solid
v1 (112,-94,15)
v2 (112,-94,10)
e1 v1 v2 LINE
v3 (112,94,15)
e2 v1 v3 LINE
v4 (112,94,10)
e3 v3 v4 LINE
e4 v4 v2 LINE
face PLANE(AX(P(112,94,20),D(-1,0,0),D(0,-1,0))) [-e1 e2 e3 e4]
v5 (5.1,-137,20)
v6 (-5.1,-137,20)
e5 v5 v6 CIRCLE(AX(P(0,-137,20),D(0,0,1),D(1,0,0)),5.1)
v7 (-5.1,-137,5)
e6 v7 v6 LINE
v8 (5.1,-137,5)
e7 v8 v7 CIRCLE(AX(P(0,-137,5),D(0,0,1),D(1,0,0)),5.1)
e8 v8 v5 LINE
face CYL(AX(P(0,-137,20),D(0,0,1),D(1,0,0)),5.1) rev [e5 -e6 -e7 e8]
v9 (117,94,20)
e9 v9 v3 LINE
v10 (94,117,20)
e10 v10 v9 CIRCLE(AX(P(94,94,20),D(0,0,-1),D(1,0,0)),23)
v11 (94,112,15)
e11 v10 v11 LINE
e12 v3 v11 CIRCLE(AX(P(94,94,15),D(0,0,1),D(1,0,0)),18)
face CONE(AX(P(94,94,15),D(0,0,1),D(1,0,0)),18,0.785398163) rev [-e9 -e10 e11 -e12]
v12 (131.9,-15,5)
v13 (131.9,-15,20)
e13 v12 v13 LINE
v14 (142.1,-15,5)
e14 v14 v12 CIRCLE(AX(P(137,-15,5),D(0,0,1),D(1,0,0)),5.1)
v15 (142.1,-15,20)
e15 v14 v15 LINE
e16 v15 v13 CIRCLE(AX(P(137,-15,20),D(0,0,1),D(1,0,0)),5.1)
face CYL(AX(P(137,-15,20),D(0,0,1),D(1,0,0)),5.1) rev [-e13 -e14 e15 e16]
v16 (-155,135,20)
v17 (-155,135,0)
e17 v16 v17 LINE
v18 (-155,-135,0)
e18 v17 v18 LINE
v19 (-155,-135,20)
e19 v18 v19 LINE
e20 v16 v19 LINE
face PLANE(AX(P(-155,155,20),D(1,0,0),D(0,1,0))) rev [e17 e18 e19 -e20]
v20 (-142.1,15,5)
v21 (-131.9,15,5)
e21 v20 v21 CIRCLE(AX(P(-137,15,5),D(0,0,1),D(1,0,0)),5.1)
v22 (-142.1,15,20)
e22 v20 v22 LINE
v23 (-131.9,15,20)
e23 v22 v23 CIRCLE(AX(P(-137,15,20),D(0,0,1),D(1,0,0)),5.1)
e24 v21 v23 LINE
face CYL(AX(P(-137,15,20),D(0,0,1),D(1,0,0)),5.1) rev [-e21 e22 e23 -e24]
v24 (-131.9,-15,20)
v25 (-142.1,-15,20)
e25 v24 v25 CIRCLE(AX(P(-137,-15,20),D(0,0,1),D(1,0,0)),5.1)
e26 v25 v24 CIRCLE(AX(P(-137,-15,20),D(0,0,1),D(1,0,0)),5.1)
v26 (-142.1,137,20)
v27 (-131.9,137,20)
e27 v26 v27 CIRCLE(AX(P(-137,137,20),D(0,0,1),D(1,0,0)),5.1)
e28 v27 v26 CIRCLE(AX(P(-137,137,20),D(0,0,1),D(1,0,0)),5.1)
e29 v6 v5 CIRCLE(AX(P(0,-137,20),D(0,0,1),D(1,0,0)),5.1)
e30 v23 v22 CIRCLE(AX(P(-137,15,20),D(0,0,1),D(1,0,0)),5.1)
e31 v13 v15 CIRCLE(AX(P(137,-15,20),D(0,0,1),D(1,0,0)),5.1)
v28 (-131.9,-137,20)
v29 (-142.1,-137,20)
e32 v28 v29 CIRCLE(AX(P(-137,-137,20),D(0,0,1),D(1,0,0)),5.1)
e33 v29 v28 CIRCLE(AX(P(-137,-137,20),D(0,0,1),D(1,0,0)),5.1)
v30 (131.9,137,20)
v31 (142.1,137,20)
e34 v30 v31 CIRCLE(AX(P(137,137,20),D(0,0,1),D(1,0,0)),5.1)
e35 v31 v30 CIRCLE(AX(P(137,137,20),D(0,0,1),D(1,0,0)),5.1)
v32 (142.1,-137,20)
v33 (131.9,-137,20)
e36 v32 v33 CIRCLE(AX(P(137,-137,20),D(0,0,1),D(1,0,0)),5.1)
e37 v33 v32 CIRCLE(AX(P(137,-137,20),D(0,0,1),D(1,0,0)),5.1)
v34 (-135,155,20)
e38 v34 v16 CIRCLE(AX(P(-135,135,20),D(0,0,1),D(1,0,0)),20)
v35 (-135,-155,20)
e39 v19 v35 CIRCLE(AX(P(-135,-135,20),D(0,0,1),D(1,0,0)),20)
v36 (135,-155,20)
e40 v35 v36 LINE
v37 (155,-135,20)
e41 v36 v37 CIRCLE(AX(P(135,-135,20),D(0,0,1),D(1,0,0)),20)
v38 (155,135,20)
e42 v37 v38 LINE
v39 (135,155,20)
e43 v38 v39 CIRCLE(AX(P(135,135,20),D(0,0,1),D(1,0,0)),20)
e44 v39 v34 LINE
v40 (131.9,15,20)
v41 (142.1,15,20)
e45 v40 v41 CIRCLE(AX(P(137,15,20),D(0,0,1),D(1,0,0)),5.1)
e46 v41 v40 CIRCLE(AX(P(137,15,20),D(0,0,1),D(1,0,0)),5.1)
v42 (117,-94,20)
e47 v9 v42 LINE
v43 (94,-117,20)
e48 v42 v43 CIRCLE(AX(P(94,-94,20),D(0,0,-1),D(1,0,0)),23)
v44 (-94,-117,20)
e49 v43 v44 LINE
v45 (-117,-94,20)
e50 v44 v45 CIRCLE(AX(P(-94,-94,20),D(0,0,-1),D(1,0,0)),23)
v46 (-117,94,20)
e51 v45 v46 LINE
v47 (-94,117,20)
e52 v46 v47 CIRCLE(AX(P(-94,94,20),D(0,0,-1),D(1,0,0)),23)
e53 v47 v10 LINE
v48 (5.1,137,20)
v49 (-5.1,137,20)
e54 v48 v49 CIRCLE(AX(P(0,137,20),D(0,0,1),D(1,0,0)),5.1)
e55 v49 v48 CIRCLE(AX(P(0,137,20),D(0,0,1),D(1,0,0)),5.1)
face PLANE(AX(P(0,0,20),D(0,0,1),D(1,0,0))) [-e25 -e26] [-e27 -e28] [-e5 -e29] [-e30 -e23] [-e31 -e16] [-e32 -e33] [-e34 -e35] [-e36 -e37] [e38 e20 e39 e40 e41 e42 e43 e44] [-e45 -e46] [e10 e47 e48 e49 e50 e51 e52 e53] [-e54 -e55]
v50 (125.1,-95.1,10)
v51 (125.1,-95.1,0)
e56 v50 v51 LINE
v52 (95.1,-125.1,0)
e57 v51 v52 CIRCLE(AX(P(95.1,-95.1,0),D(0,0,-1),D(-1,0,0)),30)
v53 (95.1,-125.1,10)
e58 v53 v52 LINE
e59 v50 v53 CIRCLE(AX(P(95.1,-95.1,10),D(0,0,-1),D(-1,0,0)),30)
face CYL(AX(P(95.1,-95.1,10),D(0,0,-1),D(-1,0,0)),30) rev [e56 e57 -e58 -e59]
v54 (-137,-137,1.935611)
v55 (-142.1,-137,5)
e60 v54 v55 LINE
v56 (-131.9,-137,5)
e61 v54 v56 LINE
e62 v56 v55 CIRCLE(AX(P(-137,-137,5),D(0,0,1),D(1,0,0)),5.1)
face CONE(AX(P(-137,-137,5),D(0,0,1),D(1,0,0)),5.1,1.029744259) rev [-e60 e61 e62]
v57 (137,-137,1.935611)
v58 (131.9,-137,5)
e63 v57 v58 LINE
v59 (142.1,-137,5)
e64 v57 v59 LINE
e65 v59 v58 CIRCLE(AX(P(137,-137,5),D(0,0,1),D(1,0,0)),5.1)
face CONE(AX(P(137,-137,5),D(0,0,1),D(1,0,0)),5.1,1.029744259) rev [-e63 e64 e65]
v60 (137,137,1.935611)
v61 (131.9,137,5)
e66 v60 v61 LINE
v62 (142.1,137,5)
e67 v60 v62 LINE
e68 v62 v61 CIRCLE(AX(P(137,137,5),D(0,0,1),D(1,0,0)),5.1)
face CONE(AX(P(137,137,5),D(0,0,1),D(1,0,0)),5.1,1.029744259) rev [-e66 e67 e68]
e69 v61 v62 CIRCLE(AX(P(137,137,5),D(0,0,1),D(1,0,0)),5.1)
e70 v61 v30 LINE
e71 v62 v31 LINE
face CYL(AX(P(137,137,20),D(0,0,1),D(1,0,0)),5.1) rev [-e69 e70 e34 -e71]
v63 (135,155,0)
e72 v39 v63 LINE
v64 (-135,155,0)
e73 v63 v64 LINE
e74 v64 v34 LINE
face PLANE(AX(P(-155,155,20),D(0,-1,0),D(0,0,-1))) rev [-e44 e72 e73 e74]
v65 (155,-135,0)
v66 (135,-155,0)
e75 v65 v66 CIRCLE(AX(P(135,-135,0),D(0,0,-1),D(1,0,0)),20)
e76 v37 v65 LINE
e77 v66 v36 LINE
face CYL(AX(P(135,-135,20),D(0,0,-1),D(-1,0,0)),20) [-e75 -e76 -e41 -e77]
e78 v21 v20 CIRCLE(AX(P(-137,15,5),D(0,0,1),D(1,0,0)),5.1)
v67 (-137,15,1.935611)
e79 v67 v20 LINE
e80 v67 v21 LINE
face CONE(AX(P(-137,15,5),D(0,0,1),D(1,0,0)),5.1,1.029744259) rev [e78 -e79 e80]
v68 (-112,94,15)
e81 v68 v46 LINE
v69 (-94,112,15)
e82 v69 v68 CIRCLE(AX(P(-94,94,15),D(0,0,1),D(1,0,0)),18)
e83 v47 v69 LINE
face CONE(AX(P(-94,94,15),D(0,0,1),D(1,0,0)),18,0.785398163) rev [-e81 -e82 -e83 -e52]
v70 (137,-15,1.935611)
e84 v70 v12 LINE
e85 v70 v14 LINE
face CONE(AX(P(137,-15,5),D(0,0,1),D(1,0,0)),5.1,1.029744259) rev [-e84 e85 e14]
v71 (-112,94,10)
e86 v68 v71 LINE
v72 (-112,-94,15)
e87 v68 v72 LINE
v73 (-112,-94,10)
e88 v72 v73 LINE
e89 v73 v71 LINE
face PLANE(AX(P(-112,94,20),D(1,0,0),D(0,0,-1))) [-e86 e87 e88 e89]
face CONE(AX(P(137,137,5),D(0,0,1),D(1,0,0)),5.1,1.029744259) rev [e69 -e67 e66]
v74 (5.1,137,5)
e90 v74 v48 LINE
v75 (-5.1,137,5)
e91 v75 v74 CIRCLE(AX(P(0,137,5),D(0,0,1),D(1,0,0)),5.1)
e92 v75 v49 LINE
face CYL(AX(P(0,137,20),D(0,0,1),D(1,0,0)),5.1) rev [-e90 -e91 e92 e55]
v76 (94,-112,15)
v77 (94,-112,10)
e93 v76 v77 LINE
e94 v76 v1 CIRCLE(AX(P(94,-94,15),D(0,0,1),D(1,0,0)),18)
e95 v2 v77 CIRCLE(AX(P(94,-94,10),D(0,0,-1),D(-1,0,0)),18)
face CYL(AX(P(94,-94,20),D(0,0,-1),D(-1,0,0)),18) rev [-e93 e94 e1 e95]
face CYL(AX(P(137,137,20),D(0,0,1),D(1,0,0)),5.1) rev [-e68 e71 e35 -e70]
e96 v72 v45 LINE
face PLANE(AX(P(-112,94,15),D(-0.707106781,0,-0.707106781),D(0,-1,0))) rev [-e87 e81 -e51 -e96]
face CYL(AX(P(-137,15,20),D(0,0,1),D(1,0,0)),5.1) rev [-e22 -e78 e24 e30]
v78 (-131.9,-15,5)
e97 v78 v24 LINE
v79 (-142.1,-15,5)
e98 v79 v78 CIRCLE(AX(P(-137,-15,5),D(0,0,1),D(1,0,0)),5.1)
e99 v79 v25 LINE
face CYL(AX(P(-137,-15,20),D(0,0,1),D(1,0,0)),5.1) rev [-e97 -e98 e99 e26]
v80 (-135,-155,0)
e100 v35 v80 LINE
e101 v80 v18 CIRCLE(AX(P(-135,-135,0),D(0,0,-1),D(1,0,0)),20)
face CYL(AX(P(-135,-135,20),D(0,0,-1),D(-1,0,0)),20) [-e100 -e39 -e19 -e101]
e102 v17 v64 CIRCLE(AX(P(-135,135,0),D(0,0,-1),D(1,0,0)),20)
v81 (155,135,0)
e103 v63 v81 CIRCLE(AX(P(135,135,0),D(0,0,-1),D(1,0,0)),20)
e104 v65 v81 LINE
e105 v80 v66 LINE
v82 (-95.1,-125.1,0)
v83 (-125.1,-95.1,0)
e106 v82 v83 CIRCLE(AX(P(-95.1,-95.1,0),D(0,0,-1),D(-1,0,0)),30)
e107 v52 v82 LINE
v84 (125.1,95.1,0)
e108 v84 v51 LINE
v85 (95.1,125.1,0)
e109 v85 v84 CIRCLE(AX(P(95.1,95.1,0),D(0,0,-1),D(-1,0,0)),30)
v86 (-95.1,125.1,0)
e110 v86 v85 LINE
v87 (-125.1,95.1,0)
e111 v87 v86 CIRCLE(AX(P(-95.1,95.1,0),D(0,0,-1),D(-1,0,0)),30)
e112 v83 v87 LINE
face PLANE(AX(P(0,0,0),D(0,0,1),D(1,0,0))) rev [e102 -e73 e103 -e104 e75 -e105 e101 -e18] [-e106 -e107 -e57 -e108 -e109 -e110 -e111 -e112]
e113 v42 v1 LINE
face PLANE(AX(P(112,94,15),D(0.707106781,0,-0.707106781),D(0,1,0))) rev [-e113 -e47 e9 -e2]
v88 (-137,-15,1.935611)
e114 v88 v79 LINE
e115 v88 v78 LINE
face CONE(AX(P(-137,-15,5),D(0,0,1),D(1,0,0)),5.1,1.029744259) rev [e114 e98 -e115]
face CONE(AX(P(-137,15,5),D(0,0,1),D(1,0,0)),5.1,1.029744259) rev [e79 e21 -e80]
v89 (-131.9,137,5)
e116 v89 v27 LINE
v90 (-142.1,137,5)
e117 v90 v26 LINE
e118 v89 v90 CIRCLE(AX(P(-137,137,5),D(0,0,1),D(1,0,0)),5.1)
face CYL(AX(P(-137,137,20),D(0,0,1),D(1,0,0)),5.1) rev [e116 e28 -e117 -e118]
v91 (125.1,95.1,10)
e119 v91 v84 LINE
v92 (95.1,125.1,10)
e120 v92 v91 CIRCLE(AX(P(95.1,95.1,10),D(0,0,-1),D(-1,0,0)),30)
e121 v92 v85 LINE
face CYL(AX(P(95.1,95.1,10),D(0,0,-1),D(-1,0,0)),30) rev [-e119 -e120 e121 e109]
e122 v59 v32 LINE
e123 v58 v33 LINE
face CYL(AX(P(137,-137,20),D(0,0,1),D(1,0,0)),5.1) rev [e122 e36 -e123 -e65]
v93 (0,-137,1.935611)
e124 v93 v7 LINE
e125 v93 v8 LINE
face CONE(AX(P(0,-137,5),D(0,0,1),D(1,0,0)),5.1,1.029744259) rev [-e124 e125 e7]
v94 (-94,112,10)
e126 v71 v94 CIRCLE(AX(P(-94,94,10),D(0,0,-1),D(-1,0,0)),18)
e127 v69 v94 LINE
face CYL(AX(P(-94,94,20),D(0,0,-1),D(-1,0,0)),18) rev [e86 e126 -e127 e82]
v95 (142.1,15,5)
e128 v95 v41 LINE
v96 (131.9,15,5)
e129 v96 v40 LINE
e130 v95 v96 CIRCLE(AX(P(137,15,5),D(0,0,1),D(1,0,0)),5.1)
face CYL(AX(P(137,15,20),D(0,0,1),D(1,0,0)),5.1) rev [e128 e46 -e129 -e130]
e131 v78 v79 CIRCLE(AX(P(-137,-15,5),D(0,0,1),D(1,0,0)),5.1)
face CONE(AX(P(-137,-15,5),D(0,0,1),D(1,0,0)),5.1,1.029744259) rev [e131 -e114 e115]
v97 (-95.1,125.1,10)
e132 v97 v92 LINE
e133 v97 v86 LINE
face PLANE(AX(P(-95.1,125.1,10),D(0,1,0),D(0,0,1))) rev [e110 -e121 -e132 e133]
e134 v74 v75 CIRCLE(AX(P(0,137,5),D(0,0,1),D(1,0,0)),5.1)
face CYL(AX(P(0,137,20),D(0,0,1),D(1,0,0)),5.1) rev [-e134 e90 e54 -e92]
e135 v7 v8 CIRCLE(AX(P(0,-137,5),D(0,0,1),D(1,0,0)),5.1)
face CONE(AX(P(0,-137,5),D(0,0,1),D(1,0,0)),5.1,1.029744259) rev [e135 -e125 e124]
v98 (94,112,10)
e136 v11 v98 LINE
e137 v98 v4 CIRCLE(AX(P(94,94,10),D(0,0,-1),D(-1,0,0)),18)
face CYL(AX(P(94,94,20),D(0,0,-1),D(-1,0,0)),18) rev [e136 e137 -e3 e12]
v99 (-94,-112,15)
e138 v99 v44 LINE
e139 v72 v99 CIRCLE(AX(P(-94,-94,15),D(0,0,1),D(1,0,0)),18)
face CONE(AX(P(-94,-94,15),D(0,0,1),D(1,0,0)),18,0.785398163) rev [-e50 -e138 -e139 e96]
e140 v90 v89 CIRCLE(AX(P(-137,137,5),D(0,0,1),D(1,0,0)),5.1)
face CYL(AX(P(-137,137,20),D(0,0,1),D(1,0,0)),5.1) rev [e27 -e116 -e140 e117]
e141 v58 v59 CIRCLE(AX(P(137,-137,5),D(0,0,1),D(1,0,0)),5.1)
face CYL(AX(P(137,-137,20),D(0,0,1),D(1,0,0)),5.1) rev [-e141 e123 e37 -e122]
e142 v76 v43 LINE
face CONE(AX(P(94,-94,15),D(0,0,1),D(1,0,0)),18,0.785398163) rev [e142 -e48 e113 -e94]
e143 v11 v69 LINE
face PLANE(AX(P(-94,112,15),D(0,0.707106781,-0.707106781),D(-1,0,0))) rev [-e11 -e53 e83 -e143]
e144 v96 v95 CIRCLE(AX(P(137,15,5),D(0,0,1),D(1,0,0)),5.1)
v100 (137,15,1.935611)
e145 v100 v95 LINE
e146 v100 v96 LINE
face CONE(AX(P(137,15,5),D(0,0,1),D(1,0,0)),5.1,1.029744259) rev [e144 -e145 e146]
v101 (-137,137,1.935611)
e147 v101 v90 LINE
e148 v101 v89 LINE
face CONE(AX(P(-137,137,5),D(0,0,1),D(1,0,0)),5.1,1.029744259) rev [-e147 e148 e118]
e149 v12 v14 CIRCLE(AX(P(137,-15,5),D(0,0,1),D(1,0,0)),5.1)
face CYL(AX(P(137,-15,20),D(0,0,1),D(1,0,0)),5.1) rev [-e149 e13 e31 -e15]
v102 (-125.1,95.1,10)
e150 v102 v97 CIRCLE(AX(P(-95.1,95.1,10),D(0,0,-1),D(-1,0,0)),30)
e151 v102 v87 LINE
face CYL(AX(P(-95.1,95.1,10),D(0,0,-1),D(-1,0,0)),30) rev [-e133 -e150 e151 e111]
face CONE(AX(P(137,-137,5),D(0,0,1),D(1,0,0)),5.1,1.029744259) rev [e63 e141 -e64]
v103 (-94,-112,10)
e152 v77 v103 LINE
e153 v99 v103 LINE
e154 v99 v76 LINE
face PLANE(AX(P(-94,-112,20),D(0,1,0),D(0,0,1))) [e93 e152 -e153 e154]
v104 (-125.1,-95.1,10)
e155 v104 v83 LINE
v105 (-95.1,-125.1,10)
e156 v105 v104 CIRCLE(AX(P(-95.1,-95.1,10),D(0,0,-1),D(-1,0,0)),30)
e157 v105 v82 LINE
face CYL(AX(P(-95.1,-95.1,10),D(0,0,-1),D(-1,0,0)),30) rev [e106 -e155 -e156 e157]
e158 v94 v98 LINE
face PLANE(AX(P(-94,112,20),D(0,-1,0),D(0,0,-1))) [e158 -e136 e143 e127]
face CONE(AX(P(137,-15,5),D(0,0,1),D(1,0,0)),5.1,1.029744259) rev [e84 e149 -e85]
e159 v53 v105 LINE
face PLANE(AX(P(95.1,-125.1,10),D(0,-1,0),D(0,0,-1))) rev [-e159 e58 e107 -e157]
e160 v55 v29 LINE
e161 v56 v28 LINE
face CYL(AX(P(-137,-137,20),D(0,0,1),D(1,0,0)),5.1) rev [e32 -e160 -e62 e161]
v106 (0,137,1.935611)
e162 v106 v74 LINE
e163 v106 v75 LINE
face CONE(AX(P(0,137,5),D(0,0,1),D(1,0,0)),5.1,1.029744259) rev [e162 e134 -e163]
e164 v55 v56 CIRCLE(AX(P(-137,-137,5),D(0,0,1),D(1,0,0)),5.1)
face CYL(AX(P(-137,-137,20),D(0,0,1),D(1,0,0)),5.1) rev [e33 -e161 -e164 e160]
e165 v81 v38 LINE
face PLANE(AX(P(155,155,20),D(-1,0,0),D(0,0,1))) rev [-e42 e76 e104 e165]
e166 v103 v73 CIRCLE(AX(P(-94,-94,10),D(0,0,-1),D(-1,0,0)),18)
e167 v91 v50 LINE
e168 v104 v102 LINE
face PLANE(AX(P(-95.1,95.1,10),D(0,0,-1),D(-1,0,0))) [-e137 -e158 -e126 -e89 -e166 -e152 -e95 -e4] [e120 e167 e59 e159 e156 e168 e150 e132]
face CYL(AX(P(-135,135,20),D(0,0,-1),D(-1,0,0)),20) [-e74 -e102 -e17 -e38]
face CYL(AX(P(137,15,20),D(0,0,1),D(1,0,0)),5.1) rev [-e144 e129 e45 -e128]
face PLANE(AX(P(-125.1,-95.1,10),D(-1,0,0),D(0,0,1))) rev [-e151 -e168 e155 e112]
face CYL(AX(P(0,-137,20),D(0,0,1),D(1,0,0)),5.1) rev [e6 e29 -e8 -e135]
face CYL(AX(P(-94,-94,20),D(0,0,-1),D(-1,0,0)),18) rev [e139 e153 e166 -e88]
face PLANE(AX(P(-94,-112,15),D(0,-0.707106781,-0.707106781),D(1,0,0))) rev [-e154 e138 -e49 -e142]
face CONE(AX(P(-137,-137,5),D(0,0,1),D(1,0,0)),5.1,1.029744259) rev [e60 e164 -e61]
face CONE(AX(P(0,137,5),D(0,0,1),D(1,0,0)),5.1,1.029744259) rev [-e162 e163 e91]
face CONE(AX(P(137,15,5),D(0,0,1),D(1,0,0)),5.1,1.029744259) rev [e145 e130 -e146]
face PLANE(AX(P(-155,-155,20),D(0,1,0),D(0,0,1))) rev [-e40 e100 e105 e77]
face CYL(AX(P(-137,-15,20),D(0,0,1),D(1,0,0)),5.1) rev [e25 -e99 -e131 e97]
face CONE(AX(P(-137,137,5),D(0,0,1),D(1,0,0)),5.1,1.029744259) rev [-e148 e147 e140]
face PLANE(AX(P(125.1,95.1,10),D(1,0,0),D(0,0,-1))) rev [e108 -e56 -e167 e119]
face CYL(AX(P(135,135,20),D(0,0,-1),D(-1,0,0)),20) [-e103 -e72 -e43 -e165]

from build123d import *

# Parameters (mm, degrees)
SKETCH_1_W              = 310
SKETCH_1_H              = 310
EXTRUDE_1_DEPTH         = 20
FILLET_1_R              = 20
CUT_EXTRUDE_1_DEPTH     = 10
HOLE_WIZARD_M12_1_D     = 10.2
HOLE_WIZARD_M12_1_DEPTH = 15
HOLE_WIZARD_M12_1_TIP   = 3.064389157
CHAMFER_1_SIZE          = 5


with BuildPart() as part:
    # 草图1 → 凸台-拉伸1 (new body)
    with BuildSketch(Plane.XY):
        Rectangle(SKETCH_1_W, SKETCH_1_H)
        with BuildLine():
            Line((-94, 112), (94, 112))
            ThreePointArc((94, 112), (106.727922061, 106.727922061), (112, 94))
            Line((112, 94), (112, -94))
            ThreePointArc((112, -94), (106.727922061, -106.727922061), (94, -112))
            Line((94, -112), (-94, -112))
            ThreePointArc((-94, -112), (-106.727922061, -106.727922061), (-112, -94))
            Line((-112, -94), (-112, 94))
            ThreePointArc((-112, 94), (-106.727922061, 106.727922061), (-94, 112))
        make_face(mode=Mode.SUBTRACT)
    extrude(amount=EXTRUDE_1_DEPTH)

    # 圆角1
    fillet_1_edges = [part.edges().sort_by_distance(p)[0] for p in [
        (155, -155, 10),
        (-155, -155, 10),
        (-155, 155, 10),
        (155, 155, 10),
    ]]
    fillet(fillet_1_edges, radius=FILLET_1_R)

    # 草图2 → 切除-拉伸1 (cut)
    with BuildSketch(Plane(origin=(0, 0, 0), x_dir=(-1, 0, 0), z_dir=(0, 0, -1))):
        with BuildLine():
            Line((125.1, -95.1), (125.1, 95.1))
            ThreePointArc((125.1, 95.1), (116.313203436, 116.313203436), (95.1, 125.1))
            Line((95.1, 125.1), (-95.1, 125.1))
            ThreePointArc((-95.1, 125.1), (-116.313203436, 116.313203436), (-125.1, 95.1))
            Line((-125.1, 95.1), (-125.1, -95.1))
            ThreePointArc((-125.1, -95.1), (-116.313203436, -116.313203436), (-95.1, -125.1))
            Line((-95.1, -125.1), (95.1, -125.1))
            ThreePointArc((95.1, -125.1), (116.313203436, -116.313203436), (125.1, -95.1))
        make_face()
    extrude(amount=-CUT_EXTRUDE_1_DEPTH, mode=Mode.SUBTRACT)

    # M12 螺纹孔1
    with Locations(Plane(origin=(-137, 137, 20), x_dir=(1, 0, 0), z_dir=(0, 0, 1))):
        with Locations((0, 0), (274, 0), (274, -274), (0, -274), (137, -274), (137, 0), (0, -122), (0, -152), (274, -122), (274, -152)):
            Hole(HOLE_WIZARD_M12_1_D / 2, depth=HOLE_WIZARD_M12_1_DEPTH)
            with Locations((0, 0, -(HOLE_WIZARD_M12_1_DEPTH + HOLE_WIZARD_M12_1_TIP / 2))):  # 118° drill point
                Cone(0, HOLE_WIZARD_M12_1_D / 2, HOLE_WIZARD_M12_1_TIP, mode=Mode.SUBTRACT)

    # 倒角1
    chamfer_1_edges = [part.edges().sort_by_distance(p)[0] for p in [
        (106.727922061, -106.727922061, 20),
        (112, 0, 20),
        (106.727922061, 106.727922061, 20),
        (0, 112, 20),
        (-106.727922061, 106.727922061, 20),
        (-112, 0, 20),
        (-106.727922061, -106.727922061, 20),
        (0, -112, 20),
    ]]
    chamfer(chamfer_1_edges, length=CHAMFER_1_SIZE)


solid = part.part
